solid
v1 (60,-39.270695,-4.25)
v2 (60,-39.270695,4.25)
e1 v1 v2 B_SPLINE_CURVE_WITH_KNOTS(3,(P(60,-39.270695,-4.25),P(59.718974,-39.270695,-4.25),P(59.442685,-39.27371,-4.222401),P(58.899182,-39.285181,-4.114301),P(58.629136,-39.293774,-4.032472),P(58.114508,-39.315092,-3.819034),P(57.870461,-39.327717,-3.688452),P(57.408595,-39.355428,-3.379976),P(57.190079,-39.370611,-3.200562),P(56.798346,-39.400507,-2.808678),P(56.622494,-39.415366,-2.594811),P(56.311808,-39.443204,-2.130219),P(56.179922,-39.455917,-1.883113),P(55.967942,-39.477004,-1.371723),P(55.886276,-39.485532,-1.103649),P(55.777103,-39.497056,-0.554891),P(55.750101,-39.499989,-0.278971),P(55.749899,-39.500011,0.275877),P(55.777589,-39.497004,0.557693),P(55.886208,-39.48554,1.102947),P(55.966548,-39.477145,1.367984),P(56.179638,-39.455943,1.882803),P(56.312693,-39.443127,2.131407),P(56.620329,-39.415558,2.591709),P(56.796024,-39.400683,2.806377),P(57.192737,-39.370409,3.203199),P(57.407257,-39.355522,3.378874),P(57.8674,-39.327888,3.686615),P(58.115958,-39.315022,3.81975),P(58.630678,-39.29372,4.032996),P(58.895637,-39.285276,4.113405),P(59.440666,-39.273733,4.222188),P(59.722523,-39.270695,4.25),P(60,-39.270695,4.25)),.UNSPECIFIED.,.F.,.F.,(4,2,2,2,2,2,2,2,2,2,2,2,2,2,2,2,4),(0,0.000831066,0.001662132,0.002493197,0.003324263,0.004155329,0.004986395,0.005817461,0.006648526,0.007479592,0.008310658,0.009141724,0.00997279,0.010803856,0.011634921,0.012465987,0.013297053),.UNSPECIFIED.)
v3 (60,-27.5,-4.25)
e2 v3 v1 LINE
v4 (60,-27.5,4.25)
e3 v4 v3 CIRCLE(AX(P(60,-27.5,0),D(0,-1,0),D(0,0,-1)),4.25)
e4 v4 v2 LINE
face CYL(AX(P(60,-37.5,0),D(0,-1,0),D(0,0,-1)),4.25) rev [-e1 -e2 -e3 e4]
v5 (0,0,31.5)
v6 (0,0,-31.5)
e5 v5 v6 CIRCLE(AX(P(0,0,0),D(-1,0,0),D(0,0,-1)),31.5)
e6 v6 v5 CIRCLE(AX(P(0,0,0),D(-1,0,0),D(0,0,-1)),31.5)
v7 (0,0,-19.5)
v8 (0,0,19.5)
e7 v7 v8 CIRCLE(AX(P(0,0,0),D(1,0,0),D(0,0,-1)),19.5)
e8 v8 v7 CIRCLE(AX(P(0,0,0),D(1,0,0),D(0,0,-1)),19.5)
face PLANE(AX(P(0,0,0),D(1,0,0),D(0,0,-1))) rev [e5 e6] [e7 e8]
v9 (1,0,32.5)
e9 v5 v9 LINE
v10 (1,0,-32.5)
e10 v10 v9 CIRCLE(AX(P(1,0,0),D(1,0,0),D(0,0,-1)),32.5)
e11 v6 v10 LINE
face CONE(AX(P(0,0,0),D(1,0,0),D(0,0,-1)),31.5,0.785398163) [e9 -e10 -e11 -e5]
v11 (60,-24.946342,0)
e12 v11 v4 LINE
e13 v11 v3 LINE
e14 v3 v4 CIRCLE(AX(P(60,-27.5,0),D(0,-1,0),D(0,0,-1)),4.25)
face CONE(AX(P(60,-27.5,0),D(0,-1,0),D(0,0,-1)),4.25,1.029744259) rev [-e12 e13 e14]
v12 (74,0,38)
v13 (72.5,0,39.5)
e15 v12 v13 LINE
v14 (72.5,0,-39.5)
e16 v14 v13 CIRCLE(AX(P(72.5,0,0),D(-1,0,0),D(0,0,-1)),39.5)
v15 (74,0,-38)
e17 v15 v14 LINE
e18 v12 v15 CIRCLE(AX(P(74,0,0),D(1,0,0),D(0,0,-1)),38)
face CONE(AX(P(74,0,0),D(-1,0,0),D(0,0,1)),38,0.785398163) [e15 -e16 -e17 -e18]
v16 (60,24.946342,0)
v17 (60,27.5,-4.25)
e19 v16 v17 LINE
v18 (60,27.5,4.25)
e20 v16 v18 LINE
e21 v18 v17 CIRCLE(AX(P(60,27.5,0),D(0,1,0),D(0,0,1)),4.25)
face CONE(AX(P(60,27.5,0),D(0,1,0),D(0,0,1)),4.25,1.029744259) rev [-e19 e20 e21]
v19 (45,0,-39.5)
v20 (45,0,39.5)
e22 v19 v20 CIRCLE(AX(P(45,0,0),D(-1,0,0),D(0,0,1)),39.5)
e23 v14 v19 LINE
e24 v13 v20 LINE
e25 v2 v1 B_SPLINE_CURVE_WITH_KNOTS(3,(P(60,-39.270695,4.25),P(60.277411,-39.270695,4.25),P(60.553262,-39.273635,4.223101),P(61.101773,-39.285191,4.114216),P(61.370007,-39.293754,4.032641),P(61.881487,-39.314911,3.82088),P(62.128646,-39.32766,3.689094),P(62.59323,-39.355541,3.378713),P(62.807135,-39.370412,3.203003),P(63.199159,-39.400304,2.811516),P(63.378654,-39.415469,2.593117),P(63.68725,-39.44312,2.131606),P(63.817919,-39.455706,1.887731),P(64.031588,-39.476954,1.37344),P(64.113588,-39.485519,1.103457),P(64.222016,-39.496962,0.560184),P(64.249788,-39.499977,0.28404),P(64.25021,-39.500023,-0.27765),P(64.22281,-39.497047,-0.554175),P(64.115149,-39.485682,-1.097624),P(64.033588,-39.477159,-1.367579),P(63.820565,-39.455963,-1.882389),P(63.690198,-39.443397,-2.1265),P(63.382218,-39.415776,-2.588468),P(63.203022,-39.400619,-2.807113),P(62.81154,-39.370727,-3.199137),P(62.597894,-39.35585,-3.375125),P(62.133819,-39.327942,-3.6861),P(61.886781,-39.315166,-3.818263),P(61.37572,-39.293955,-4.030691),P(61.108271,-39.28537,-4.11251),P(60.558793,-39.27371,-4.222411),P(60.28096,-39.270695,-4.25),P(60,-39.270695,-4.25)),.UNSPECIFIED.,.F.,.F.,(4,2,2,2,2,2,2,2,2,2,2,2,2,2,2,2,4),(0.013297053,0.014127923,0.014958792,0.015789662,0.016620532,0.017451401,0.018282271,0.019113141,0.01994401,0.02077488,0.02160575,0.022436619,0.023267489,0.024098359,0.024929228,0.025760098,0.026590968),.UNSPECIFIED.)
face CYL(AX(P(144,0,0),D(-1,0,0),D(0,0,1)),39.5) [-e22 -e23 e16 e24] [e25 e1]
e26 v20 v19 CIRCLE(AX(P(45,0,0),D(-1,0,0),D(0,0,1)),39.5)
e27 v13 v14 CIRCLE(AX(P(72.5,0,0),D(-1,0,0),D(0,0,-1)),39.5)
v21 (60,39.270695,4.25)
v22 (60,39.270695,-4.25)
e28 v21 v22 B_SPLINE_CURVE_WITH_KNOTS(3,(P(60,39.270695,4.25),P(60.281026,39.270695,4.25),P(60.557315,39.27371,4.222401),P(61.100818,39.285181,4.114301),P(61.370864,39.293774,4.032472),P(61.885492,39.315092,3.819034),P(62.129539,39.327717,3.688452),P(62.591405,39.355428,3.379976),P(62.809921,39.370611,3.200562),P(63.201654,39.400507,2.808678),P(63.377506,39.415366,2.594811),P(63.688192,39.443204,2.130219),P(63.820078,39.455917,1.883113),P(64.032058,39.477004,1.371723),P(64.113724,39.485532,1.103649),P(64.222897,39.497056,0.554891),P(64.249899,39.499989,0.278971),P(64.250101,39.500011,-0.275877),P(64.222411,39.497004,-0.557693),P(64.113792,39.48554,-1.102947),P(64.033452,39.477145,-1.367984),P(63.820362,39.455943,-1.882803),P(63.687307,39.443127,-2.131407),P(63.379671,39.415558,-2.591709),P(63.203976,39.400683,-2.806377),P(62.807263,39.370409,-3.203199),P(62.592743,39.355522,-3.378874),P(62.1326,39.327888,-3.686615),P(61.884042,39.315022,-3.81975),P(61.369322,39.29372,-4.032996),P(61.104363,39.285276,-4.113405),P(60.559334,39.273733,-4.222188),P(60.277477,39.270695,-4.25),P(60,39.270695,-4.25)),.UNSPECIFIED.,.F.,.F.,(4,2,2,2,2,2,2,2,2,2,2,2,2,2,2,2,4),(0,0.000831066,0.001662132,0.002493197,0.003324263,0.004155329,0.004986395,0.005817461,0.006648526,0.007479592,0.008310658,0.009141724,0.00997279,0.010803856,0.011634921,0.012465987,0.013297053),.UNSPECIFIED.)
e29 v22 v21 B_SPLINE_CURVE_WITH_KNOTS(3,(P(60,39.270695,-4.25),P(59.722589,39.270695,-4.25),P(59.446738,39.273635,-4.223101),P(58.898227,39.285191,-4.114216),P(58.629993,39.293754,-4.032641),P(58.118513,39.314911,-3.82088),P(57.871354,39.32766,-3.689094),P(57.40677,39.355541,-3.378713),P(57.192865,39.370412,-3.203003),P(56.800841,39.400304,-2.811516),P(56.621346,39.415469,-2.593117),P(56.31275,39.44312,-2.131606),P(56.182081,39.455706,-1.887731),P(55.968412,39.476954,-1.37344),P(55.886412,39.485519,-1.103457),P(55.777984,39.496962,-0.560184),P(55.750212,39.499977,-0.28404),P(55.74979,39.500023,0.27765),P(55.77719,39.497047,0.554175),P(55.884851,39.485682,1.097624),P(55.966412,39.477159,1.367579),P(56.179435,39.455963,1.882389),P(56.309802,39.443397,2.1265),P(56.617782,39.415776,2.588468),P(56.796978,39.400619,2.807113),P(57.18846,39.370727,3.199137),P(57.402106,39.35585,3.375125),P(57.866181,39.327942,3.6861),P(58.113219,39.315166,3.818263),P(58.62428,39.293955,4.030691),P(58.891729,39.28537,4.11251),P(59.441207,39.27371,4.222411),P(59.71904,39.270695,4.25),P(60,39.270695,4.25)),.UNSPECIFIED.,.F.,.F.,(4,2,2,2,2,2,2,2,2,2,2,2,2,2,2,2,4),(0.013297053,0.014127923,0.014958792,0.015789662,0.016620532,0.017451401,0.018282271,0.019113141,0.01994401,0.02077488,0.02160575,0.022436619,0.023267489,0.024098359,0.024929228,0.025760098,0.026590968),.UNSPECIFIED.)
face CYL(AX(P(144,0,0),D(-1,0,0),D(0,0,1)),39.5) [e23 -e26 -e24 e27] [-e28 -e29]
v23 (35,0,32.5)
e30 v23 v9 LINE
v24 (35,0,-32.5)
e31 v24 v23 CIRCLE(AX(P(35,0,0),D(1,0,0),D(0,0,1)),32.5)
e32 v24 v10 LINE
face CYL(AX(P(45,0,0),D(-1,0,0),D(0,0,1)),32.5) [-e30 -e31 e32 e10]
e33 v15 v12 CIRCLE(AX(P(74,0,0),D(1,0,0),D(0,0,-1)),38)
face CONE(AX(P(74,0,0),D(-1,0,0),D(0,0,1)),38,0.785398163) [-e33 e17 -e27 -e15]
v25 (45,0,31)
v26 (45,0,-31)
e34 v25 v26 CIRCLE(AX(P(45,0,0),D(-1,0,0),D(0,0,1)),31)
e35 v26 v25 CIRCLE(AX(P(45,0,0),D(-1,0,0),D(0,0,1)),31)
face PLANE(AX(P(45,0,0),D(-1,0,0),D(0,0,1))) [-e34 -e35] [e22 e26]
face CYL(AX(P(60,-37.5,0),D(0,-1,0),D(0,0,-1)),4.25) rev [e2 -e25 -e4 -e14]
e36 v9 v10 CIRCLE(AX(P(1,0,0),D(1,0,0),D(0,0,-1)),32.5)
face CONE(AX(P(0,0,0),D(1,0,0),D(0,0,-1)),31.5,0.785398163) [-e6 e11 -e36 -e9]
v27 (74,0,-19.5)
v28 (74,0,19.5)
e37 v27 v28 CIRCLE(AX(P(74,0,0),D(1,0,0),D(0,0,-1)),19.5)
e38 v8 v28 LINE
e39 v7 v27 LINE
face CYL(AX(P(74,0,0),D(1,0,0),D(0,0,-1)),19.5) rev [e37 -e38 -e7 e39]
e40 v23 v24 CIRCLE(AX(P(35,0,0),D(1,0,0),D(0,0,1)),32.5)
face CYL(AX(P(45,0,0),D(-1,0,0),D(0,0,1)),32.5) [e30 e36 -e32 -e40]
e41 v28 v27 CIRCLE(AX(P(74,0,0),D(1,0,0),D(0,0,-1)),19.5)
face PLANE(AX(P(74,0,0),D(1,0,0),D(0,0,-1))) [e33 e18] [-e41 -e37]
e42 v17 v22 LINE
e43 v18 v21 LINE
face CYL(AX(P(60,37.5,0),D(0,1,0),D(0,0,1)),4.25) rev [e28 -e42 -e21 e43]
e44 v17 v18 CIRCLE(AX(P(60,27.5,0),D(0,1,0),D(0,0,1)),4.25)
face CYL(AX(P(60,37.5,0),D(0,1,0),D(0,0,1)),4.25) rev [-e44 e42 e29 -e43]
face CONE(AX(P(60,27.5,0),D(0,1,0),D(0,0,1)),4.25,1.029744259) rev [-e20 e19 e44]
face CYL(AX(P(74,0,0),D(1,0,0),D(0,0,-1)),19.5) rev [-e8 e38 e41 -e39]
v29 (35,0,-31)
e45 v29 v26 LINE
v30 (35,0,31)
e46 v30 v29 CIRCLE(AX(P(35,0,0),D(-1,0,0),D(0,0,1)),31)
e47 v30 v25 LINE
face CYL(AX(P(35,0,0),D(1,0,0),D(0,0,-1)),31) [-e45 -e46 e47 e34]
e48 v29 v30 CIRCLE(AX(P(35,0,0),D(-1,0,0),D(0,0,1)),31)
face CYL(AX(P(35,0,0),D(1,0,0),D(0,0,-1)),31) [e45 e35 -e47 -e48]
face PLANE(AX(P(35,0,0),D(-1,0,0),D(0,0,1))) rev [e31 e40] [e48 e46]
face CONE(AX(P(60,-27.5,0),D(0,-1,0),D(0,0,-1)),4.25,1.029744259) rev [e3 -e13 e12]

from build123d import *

# Parameters (mm, degrees)
SKETCH1_R              = 39.5
BOSS_EXTRUDE1_DEPTH    = 144
SKETCH2_OUTSIDE_W      = 117.452
SKETCH2_OUTSIDE_H      = 117.452
SKETCH2_OUTSIDE_R      = 22.5
CUT_EXTRUDE1_DEPTH     = 70
SKETCH4_OUTSIDE_W      = 117.452
SKETCH4_OUTSIDE_H      = 117.452
SKETCH4_OUTSIDE_R      = 32.5
CUT_EXTRUDE3_DEPTH     = 45
SKETCH6_OUTSIDE_W      = 117.452
SKETCH6_OUTSIDE_H      = 117.452
SKETCH6_OUTSIDE_R      = 31
CUT_EXTRUDE5_DEPTH     = 10
CHAMFER1_SIZE          = 1
CHAMFER7_SIZE          = 1.5
SKETCH12_R             = 4.25
CUT_EXTRUDE8_DEPTH     = 2
SKETCH15_R             = 63.738357407
CUT_EXTRUDE9_DEPTH     = 70
M42X3_0_TAPPED_HOLE1_D = 39


with BuildPart() as part:
    # Sketch1 → Boss-Extrude1 (new body)
    with BuildSketch(Plane(origin=(0, 0, 0), x_dir=(0, 0, -1), z_dir=(1, 0, 0))):
        Circle(SKETCH1_R)
    extrude(amount=BOSS_EXTRUDE1_DEPTH)

    # Sketch2 outside → Cut-Extrude1 (cut)
    with BuildSketch(Plane(origin=(144, 0, 0), x_dir=(0, 0, -1), z_dir=(1, 0, 0))):
        Rectangle(SKETCH2_OUTSIDE_W, SKETCH2_OUTSIDE_H)
        Circle(SKETCH2_OUTSIDE_R, mode=Mode.SUBTRACT)
    extrude(amount=-CUT_EXTRUDE1_DEPTH, mode=Mode.SUBTRACT)

    # Sketch4 outside → Cut-Extrude3 (cut)
    with BuildSketch(Plane.ZY):
        Rectangle(SKETCH4_OUTSIDE_W, SKETCH4_OUTSIDE_H)
        Circle(SKETCH4_OUTSIDE_R, mode=Mode.SUBTRACT)
    extrude(amount=-CUT_EXTRUDE3_DEPTH, mode=Mode.SUBTRACT)

    # Sketch6 outside → Cut-Extrude5 (cut)
    with BuildSketch(Plane.ZY.offset(-45)):
        Rectangle(SKETCH6_OUTSIDE_W, SKETCH6_OUTSIDE_H)
        Circle(SKETCH6_OUTSIDE_R, mode=Mode.SUBTRACT)
    extrude(amount=CUT_EXTRUDE5_DEPTH, mode=Mode.SUBTRACT)

    # Chamfer1
    chamfer1_edges = [part.edges().sort_by_distance(p)[0] for p in [
        (144, 0, 22.5),
        (0, 0, -32.5),
    ]]
    chamfer(chamfer1_edges, length=CHAMFER1_SIZE)

    # Chamfer7
    chamfer7_edges = [part.edges().sort_by_distance(p)[0] for p in [
        (74, 0, 39.5),
    ]]
    chamfer(chamfer7_edges, length=CHAMFER7_SIZE)

    # Sketch12 → Cut-Extrude8 (cut)
    with BuildSketch(Plane(origin=(0, -39.5, 0), x_dir=(-1, 0, 0), z_dir=(0, -1, 0))):
        with Locations(Location((-60, 0, 0), (0, 0, 90))):
            Circle(SKETCH12_R)
    cut_extrude8 = extrude(amount=-CUT_EXTRUDE8_DEPTH, mode=Mode.SUBTRACT)

    # Sketch14 → M10 Tapped Hole1 (revolve, cut)
    with BuildSketch(Plane(origin=(60, -37.5, 0), x_dir=(0, 0, -1), z_dir=(1, 0, 0))):
        Polygon((0, 0), (0, 12.553657631), (4.25, 10), (4.25, 0), align=None)
    m10_tapped_hole1 = revolve(axis=Axis((60, -43.85, 0), (0, 1, 0)), mode=Mode.SUBTRACT)

    # Mirror1: Cut-Extrude8, M10 Tapped Hole1 across plane
    add(cut_extrude8.mirror(Plane.ZX), mode=Mode.SUBTRACT)
    add(m10_tapped_hole1.mirror(Plane.ZX), mode=Mode.SUBTRACT)

    # Sketch15 → Cut-Extrude9 (cut)
    with BuildSketch(Plane(origin=(144, 0, 0), x_dir=(0, 0, -1), z_dir=(1, 0, 0))):
        Circle(SKETCH15_R)
    extrude(amount=-CUT_EXTRUDE9_DEPTH, mode=Mode.SUBTRACT)

    # M42x3.0 Tapped Hole1 (through all)
    with Locations(Plane(origin=(74, 0, 0), x_dir=(0, 0, -1), z_dir=(1, 0, 0))):
        with Locations((0, 0)):
            Hole(M42X3_0_TAPPED_HOLE1_D / 2)


solid = part.part
